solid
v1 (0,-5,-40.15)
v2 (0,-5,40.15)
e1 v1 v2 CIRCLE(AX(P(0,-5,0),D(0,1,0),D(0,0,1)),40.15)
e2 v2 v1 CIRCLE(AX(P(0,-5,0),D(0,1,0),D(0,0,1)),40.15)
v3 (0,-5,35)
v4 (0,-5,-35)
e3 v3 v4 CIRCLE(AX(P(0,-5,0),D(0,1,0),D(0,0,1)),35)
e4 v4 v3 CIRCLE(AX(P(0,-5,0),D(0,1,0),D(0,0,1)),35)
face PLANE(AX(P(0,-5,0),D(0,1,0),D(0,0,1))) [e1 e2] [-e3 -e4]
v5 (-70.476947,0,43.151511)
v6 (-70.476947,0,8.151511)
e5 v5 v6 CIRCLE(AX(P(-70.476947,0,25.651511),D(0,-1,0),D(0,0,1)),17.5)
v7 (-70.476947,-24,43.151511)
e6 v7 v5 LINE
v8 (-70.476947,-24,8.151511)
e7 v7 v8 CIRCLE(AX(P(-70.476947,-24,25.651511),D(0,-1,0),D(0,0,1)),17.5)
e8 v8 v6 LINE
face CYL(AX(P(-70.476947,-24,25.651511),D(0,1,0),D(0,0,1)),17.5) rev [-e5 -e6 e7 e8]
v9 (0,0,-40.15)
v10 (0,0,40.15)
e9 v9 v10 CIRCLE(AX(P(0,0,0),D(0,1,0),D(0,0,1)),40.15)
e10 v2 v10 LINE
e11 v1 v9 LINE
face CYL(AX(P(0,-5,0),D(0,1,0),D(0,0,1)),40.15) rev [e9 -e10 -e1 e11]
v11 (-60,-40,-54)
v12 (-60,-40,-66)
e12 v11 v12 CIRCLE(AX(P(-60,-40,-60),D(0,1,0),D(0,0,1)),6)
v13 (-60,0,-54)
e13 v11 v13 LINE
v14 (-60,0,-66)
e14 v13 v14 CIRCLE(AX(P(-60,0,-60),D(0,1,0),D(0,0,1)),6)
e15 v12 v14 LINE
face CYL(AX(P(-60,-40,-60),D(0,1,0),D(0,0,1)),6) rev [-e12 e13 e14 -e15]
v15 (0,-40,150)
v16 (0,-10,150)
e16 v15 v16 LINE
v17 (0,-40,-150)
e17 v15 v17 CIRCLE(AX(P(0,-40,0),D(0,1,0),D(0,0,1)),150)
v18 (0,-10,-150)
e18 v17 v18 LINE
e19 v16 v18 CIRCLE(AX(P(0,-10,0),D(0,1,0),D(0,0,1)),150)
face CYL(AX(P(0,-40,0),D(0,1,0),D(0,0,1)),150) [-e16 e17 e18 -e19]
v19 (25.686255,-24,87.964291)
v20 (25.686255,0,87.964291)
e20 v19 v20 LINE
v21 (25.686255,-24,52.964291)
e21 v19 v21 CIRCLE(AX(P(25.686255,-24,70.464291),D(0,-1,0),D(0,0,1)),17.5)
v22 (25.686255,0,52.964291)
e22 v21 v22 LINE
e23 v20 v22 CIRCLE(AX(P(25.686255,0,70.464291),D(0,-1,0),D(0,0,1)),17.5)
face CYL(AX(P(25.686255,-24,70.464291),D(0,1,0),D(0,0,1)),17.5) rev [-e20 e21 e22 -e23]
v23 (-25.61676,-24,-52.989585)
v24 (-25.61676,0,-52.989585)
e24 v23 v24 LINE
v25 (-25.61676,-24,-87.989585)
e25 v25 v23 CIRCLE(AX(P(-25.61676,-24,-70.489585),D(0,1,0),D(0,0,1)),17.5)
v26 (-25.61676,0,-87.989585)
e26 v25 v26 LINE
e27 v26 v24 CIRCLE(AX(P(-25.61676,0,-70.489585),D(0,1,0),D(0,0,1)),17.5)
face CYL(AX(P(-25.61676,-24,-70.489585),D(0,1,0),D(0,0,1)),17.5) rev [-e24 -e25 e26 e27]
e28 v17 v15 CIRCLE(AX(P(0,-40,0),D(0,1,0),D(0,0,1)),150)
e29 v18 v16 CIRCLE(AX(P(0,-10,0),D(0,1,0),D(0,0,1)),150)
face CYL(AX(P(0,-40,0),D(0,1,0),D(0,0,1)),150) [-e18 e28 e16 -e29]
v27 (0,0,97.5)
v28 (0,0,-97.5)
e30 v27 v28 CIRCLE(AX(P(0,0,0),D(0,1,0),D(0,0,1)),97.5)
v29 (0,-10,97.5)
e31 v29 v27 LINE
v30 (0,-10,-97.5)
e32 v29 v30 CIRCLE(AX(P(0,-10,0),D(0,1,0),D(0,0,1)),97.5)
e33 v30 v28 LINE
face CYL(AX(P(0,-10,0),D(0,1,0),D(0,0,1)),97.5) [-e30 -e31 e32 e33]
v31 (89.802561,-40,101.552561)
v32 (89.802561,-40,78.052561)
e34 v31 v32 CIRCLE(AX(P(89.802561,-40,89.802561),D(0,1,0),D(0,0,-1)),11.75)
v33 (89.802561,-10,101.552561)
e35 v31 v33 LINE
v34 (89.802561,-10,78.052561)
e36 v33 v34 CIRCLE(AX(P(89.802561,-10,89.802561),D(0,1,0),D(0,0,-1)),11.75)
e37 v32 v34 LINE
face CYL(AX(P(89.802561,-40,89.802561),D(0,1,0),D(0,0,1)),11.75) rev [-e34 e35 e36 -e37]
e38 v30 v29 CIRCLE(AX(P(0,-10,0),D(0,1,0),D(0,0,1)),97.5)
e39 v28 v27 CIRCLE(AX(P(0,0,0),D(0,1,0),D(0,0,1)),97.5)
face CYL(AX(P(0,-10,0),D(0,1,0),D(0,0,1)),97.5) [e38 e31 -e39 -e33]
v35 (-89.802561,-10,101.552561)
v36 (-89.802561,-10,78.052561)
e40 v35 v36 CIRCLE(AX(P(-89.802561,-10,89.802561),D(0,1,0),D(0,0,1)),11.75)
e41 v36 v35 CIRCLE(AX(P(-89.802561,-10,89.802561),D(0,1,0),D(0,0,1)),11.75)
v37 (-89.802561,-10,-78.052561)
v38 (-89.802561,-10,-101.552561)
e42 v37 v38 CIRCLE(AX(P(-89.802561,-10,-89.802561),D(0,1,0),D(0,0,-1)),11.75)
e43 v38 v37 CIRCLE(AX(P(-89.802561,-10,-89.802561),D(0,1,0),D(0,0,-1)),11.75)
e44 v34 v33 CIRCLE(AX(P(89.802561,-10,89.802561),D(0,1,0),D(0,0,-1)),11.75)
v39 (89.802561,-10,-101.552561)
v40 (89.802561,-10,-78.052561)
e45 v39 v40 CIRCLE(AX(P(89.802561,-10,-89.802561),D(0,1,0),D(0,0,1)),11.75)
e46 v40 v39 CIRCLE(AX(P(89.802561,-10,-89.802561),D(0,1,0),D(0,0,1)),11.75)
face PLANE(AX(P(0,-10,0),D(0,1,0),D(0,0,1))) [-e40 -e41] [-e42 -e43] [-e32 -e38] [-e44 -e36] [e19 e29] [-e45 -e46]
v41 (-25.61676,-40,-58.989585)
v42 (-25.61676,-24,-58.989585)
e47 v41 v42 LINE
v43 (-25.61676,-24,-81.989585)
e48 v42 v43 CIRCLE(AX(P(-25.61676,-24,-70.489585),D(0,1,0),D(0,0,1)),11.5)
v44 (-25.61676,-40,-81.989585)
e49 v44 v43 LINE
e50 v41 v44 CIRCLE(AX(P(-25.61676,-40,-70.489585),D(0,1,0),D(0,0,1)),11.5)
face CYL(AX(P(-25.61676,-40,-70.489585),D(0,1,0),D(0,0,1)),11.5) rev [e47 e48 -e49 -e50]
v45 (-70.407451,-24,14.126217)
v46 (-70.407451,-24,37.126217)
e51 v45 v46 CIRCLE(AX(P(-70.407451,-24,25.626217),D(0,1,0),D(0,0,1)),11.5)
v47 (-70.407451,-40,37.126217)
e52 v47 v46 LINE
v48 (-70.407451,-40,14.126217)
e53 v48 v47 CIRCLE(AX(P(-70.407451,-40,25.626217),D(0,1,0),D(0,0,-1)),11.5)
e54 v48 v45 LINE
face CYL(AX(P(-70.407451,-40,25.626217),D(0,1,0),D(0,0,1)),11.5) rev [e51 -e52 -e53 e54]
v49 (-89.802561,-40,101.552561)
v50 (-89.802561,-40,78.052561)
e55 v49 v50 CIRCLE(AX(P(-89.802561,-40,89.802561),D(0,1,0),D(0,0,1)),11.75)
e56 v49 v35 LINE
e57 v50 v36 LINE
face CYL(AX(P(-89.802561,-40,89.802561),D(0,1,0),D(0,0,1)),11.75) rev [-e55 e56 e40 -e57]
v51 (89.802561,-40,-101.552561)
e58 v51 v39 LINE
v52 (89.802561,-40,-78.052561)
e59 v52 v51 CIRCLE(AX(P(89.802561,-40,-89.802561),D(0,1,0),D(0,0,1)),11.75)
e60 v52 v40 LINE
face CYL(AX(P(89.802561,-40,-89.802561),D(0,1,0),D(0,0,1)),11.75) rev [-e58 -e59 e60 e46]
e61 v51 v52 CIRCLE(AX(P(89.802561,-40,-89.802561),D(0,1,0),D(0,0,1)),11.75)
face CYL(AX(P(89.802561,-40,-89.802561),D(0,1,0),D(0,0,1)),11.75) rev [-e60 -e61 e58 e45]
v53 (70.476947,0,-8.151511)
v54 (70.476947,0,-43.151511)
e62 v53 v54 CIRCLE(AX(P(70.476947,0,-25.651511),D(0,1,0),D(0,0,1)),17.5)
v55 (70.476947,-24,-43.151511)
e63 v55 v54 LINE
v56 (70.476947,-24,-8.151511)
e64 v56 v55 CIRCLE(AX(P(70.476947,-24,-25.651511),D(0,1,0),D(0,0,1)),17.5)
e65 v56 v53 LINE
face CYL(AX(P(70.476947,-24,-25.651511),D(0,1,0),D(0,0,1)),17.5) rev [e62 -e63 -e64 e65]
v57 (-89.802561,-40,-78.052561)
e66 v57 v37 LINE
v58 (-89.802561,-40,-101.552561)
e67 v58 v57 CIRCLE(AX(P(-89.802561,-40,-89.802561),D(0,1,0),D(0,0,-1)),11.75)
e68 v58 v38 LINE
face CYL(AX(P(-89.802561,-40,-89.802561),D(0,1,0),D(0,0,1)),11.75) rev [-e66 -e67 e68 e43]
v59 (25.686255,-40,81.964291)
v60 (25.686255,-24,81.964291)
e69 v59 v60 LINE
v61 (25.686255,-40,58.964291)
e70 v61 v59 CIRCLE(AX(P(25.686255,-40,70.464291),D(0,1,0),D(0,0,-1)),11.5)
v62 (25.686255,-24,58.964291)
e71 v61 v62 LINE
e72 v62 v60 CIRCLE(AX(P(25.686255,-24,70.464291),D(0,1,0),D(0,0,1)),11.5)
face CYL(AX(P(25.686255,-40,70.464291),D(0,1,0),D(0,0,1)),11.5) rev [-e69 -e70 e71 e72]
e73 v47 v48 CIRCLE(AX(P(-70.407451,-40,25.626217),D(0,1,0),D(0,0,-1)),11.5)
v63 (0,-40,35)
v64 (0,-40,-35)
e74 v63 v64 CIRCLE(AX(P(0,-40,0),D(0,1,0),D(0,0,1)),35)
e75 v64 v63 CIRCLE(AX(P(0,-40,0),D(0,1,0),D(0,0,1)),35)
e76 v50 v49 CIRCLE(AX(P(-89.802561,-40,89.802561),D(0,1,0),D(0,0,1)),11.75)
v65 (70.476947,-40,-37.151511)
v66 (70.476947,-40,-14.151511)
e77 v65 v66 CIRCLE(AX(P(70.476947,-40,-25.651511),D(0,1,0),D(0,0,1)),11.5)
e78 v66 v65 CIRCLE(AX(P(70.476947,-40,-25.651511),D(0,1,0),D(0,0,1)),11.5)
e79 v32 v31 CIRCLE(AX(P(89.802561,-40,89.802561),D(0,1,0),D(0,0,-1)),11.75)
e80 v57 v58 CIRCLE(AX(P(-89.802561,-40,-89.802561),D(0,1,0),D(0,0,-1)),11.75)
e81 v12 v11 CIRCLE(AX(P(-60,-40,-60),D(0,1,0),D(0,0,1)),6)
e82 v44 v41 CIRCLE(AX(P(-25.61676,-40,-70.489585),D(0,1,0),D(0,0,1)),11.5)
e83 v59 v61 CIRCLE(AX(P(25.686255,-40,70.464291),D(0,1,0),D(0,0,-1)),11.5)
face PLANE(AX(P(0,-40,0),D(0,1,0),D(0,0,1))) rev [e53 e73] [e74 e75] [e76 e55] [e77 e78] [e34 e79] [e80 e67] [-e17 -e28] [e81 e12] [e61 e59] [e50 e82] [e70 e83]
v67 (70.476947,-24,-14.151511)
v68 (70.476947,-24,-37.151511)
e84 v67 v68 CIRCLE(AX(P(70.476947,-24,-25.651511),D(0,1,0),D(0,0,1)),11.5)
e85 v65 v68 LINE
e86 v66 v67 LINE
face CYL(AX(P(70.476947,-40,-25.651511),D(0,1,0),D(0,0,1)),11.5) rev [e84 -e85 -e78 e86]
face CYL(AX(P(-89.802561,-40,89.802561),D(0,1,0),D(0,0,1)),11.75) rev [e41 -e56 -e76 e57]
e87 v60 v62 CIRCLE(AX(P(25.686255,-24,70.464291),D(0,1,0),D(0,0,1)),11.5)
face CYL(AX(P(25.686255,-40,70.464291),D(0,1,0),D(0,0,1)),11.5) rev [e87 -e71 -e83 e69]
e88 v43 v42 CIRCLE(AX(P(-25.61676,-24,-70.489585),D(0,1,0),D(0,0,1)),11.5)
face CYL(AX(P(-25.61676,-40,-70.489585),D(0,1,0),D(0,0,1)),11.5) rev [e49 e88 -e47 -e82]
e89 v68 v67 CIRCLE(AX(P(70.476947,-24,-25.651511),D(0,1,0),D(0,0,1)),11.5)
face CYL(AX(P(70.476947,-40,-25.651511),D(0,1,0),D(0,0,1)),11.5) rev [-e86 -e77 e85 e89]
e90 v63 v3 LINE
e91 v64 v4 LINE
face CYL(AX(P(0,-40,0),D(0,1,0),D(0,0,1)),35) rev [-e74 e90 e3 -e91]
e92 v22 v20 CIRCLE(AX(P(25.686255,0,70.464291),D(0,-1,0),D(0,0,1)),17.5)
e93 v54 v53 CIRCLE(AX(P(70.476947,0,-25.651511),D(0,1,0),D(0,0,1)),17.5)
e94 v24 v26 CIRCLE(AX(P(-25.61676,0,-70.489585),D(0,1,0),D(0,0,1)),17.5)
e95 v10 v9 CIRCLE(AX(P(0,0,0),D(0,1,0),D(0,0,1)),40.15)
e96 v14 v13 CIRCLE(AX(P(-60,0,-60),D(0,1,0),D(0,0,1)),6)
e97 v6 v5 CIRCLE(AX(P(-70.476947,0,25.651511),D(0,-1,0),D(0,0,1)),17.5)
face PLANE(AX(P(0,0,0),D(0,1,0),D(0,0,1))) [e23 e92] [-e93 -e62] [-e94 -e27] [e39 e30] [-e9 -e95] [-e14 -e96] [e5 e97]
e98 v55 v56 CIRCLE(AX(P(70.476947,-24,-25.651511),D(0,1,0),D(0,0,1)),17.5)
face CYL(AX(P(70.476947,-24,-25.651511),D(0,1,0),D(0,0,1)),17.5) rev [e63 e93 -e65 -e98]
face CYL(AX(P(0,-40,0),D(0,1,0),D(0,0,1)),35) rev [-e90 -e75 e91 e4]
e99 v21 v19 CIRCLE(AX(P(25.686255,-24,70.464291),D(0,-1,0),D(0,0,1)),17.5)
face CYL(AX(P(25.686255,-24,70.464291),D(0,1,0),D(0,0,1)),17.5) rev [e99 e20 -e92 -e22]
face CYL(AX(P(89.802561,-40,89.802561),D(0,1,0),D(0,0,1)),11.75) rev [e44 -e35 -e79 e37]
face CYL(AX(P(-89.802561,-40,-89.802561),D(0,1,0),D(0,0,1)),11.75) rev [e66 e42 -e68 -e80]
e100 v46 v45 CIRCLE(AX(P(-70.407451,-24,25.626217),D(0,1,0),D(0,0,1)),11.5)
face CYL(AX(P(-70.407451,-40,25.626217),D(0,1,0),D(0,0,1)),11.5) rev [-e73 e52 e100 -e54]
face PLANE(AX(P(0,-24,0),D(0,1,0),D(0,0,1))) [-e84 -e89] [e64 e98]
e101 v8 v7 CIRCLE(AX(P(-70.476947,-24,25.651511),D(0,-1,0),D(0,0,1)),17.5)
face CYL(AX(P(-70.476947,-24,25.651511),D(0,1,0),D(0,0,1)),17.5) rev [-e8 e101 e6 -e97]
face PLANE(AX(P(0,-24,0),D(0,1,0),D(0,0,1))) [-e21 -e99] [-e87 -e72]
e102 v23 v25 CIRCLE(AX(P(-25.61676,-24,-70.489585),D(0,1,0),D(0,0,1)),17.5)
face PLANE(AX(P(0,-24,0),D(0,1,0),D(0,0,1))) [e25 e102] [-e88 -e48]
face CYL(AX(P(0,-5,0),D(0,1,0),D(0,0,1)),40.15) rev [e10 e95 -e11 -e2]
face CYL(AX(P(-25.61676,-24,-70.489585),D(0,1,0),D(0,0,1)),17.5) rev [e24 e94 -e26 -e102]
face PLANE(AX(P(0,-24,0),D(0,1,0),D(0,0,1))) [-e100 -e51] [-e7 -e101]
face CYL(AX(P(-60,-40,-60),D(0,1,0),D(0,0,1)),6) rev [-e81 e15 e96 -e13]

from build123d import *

# Parameters (mm, degrees)
FLANGE_DISC_SKETCH_300_R         = 150
FLANGE_DISC_300X40_DEPTH         = 40
BORE_SKETCH_70_R                 = 35
BORE_70_THROUGH_DEPTH            = 40
BORE_RECESS_SKETCH_80_3_R        = 40.15
BORE_RECESS_SKETCH_80_3_R_2      = 35
BORE_RECESS_80_3X5_DEPTH         = 5
RAISED_FACE_STEP_SKETCH_R        = 150
RAISED_FACE_STEP_SKETCH_R_2      = 97.5
RAISED_FACE_STEP_195X10_DEPTH    = 10
OUTER_BOLT_HOLES_SKETCH_PCD254_R = 11.75
OUTER_BOLT_HOLES_PCD254_DEPTH    = 215.242852856
INNER_HOLES_SKETCH_R             = 17.5
INNER_HOLES_CUT_24_DEEP_DEPTH    = 24
INNER_HOLE_SECONDARY_SKETCH_R    = 11.5
INNER_HOLE_SECONDARY_CUT_DEPTH   = 216.870331449
SMALL_HOLE_SKETCH_12_R           = 6
SMALL_HOLE_12_DEPTH              = 216.870331449


with BuildPart() as part:
    # Flange Disc Sketch Ø300 → Flange Disc Ø300x40 (new body)
    with BuildSketch(Plane(origin=(0, 0, 0), x_dir=(1, 0, 0), z_dir=(0, 1, 0))):
        with Locations(Location((0, 0, 0), (0, 0, 270))):
            Circle(FLANGE_DISC_SKETCH_300_R)
    extrude(amount=-FLANGE_DISC_300X40_DEPTH)

    # Bore Sketch Ø70 → Bore Ø70 Through (cut)
    with BuildSketch(Plane(origin=(0, 0, 0), x_dir=(1, 0, 0), z_dir=(0, 1, 0))):
        with Locations(Location((0, 0, 0), (0, 0, 270))):
            Circle(BORE_SKETCH_70_R)
    extrude(amount=-BORE_70_THROUGH_DEPTH, mode=Mode.SUBTRACT)

    # Bore Recess Sketch Ø80.3 → Bore Recess Ø80.3x5 (cut)
    with BuildSketch(Plane(origin=(0, 0, 0), x_dir=(1, 0, 0), z_dir=(0, 1, 0))):
        with Locations(Location((0, 0, 0), (0, 0, 270))):
            Circle(BORE_RECESS_SKETCH_80_3_R)
        with Locations(Location((0, 0, 0), (0, 0, 270))):
            Circle(BORE_RECESS_SKETCH_80_3_R_2, mode=Mode.SUBTRACT)
    extrude(amount=-BORE_RECESS_80_3X5_DEPTH, mode=Mode.SUBTRACT)

    # Raised Face Step Sketch → Raised Face Step Ø195x10 (cut)
    with BuildSketch(Plane(origin=(0, 0, 0), x_dir=(1, 0, 0), z_dir=(0, 1, 0))):
        with Locations(Location((0, 0, 0), (0, 0, 270))):
            Circle(RAISED_FACE_STEP_SKETCH_R)
        with Locations(Location((0, 0, 0), (0, 0, 270))):
            Circle(RAISED_FACE_STEP_SKETCH_R_2, mode=Mode.SUBTRACT)
    extrude(amount=-RAISED_FACE_STEP_195X10_DEPTH, mode=Mode.SUBTRACT)

    # Outer Bolt Holes Sketch PCD254 → Outer Bolt Holes PCD254 (cut, through all)
    with BuildSketch(Plane(origin=(0, -10, 0), x_dir=(1, 0, 0), z_dir=(0, 1, 0))):
        with Locations(Location((89.802561211, 89.802561211, 0), (0, 0, 270))):
            Circle(OUTER_BOLT_HOLES_SKETCH_PCD254_R)
        with Locations(Location((-89.802561211, 89.802561211, 0), (0, 0, 90))):
            Circle(OUTER_BOLT_HOLES_SKETCH_PCD254_R)
        with Locations(Location((-89.802561211, -89.802561211, 0), (0, 0, 270))):
            Circle(OUTER_BOLT_HOLES_SKETCH_PCD254_R)
        with Locations(Location((89.802561211, -89.802561211, 0), (0, 0, 90))):
            Circle(OUTER_BOLT_HOLES_SKETCH_PCD254_R)
    extrude(amount=-OUTER_BOLT_HOLES_PCD254_DEPTH, mode=Mode.SUBTRACT)

    # Inner Holes Sketch → Inner Holes Cut 24 Deep (cut)
    with BuildSketch(Plane(origin=(0, 0, 0), x_dir=(1, 0, 0), z_dir=(0, 1, 0))):
        with Locations(Location((-70.476946559, -25.651510749, 0), (0, 0, 270))):
            Circle(INNER_HOLES_SKETCH_R)
        with Locations(Location((70.476946559, 25.651510749, 0), (0, 0, 270))):
            Circle(INNER_HOLES_SKETCH_R)
        with Locations(Location((-25.616759959, 70.489585112, 0), (0, 0, 270))):
            Circle(INNER_HOLES_SKETCH_R)
        with Locations(Location((25.686255305, -70.464290874, 0), (0, 0, 270))):
            Circle(INNER_HOLES_SKETCH_R)
    extrude(amount=-INNER_HOLES_CUT_24_DEEP_DEPTH, mode=Mode.SUBTRACT)

    # Inner Hole Secondary Sketch → Inner Hole Secondary Cut (cut, through all)
    with BuildSketch(Plane(origin=(0, 0, 0), x_dir=(1, 0, 0), z_dir=(0, 1, 0))):
        with Locations(Location((70.476946559, 25.651510749, 0), (0, 0, 270))):
            Circle(INNER_HOLE_SECONDARY_SKETCH_R)
        with Locations(Location((-70.407451213, -25.626216512, 0), (0, 0, 270))):
            Circle(INNER_HOLE_SECONDARY_SKETCH_R)
        with Locations(Location((-25.616759959, 70.489585112, 0), (0, 0, 270))):
            Circle(INNER_HOLE_SECONDARY_SKETCH_R)
        with Locations(Location((25.686255305, -70.464290874, 0), (0, 0, 270))):
            Circle(INNER_HOLE_SECONDARY_SKETCH_R)
    extrude(amount=-INNER_HOLE_SECONDARY_CUT_DEPTH, mode=Mode.SUBTRACT)

    # Small Hole Sketch Ø12 → Small Hole Ø12 (cut, through all)
    with BuildSketch(Plane(origin=(0, 0, 0), x_dir=(1, 0, 0), z_dir=(0, 1, 0))):
        with Locations(Location((-60, 60, 0), (0, 0, 270))):
            Circle(SMALL_HOLE_SKETCH_12_R)
    extrude(amount=-SMALL_HOLE_12_DEPTH, mode=Mode.SUBTRACT)


solid = part.part
